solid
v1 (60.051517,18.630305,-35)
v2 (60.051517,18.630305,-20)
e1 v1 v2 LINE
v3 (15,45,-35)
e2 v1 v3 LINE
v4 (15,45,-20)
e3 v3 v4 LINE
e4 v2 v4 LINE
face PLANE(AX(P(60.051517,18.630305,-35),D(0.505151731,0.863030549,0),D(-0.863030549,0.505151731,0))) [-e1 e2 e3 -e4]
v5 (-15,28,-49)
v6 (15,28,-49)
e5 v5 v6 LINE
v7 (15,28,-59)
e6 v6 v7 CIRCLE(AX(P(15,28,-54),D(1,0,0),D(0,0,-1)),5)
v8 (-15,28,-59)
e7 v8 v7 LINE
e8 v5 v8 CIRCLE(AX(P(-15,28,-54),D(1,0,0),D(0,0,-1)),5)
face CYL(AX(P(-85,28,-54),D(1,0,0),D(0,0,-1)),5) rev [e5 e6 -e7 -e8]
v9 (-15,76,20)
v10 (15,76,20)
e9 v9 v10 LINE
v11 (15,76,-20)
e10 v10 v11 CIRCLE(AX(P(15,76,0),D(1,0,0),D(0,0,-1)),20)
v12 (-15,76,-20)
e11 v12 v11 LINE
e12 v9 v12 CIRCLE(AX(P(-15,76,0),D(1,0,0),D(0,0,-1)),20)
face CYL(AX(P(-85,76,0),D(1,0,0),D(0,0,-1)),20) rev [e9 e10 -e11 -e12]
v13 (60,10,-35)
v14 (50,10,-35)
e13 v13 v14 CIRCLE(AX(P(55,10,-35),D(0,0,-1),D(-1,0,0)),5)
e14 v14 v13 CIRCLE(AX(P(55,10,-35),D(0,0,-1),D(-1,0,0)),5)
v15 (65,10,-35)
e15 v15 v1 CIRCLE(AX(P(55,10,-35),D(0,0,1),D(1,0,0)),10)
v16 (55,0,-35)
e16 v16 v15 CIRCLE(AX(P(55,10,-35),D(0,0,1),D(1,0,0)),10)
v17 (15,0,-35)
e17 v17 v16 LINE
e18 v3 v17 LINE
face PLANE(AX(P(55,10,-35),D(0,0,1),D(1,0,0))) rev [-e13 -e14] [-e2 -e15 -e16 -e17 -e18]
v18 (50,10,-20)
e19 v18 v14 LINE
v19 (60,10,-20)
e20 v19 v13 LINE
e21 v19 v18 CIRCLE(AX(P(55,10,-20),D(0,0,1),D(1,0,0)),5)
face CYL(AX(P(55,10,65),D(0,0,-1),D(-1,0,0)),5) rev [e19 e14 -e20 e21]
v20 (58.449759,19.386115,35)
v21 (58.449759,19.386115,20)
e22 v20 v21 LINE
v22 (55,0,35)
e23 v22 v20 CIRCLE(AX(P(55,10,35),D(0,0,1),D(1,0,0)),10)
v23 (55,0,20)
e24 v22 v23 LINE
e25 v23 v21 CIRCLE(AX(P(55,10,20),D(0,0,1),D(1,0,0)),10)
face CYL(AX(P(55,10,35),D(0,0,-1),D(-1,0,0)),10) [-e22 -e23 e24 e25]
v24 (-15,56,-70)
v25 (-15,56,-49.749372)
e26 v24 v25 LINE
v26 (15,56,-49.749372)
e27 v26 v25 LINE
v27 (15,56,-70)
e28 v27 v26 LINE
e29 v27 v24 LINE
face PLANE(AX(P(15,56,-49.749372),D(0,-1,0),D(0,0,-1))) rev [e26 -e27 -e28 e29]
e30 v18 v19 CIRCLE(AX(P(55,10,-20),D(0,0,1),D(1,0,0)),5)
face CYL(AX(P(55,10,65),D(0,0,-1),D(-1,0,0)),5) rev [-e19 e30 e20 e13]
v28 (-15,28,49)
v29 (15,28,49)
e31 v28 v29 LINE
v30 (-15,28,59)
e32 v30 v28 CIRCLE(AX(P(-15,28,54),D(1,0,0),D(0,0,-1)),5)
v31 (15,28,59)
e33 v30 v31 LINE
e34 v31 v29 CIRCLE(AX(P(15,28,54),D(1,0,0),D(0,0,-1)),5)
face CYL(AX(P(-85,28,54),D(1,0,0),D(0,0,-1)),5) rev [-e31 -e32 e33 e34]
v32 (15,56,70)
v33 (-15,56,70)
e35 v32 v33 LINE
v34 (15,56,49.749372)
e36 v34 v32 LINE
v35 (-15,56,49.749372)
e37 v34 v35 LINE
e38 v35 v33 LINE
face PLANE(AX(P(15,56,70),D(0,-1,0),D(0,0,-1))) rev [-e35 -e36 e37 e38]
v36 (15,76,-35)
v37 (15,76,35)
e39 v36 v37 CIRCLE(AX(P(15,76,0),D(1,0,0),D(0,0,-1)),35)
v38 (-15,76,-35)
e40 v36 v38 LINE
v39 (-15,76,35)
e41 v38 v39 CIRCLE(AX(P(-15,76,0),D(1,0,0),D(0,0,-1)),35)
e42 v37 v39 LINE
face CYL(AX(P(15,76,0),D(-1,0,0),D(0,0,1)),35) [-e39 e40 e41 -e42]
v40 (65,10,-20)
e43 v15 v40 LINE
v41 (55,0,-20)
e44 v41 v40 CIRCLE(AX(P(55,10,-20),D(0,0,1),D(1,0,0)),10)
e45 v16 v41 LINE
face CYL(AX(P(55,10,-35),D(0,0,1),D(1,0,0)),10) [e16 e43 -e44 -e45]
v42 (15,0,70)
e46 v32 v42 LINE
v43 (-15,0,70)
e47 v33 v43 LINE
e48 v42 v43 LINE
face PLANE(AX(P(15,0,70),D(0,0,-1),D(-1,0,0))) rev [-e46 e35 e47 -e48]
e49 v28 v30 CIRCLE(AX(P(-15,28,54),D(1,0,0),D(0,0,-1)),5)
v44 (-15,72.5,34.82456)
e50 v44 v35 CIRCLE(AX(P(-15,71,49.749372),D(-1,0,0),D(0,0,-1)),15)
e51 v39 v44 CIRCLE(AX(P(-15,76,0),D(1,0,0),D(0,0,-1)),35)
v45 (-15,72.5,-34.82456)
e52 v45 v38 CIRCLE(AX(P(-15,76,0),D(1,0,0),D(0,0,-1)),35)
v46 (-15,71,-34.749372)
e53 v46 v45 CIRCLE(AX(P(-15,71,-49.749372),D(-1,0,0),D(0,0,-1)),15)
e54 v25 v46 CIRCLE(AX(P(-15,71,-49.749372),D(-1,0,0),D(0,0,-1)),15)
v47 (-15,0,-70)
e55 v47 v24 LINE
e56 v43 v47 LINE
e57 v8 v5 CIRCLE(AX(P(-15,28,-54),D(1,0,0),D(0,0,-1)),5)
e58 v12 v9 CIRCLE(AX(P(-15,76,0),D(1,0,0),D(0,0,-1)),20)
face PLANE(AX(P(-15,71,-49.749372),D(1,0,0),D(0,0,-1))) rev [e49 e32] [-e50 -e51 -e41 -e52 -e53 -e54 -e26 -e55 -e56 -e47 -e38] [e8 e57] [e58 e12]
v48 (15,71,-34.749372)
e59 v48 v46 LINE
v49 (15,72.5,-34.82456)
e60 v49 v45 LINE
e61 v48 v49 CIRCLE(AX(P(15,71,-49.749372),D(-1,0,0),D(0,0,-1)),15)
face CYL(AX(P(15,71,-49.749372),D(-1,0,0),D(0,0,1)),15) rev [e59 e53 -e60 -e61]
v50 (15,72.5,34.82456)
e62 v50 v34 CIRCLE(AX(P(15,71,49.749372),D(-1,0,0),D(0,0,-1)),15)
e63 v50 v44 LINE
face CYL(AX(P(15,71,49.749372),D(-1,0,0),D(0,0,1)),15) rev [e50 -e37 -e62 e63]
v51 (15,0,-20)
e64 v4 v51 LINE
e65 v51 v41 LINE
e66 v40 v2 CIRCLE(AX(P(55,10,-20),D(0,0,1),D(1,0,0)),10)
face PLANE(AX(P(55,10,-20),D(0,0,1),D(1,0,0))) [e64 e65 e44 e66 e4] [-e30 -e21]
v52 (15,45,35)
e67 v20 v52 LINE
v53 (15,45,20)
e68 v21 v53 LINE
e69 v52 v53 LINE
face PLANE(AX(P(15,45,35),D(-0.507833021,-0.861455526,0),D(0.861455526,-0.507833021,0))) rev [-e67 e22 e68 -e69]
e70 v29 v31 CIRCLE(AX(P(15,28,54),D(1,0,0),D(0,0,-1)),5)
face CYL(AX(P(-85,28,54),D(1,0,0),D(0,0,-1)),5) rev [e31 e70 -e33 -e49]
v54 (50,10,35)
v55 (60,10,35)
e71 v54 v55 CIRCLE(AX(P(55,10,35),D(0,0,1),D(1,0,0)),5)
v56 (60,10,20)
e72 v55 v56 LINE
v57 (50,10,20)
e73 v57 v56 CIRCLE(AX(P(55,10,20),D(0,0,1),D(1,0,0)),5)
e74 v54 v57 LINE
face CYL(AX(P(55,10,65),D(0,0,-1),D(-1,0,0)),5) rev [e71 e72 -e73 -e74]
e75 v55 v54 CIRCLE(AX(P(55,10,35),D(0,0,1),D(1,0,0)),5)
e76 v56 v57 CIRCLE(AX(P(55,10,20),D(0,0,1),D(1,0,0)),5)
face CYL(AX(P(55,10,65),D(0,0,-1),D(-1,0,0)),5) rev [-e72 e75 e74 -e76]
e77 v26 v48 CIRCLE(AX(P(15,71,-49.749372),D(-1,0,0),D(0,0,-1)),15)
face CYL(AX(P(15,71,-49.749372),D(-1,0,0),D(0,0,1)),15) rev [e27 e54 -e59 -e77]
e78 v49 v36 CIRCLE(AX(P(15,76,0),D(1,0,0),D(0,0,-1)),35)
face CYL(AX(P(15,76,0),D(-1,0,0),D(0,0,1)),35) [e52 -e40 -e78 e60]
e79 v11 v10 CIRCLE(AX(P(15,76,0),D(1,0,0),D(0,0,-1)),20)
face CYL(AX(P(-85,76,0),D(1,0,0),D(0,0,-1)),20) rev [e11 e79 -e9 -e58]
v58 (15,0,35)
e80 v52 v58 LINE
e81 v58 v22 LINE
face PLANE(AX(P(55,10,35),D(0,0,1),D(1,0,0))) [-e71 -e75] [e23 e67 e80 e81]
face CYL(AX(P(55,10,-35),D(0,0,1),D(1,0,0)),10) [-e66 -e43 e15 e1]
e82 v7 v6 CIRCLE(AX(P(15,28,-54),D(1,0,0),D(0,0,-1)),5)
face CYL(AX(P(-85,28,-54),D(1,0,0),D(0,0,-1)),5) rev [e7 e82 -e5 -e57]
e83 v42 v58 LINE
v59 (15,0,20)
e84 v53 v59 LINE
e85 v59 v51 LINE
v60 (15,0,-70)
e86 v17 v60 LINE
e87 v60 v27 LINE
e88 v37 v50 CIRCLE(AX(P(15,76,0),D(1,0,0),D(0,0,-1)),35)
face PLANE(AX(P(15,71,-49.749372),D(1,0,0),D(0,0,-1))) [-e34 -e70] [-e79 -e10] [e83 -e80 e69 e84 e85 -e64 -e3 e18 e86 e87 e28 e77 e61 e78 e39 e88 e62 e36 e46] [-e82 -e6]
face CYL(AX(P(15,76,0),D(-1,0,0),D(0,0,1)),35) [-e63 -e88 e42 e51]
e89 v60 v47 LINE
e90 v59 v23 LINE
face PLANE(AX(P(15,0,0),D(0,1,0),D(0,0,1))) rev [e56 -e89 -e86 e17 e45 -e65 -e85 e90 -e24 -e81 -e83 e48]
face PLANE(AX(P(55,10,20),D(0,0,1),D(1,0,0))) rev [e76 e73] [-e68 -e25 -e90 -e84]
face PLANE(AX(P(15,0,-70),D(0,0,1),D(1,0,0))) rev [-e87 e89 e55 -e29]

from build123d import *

# Parameters (mm, degrees)
PILLOW_BLOCK_BASE_DEPTH = 15
LUG_ARM_1_DEPTH         = 15
LUG_START               = -15
LUG_ARM_2_DEPTH         = 15
LUG_PIN_HOLE_SKETCH_R   = 5
LUG_PIN_HOLE_DEPTH      = 100
MOUNTING_HOLES_SKETCH_R = 5
MOUNTING_HOLES_2X_DEPTH = 100
SHAFT_BORE_SKETCH_R     = 20
SHAFT_BORE_DEPTH        = 100


with BuildPart() as part:
    # Base Profile Sketch → Pillow Block Base (new, symmetric)
    with BuildSketch(Plane(origin=(0, 0, 0), x_dir=(0, 0, -1), z_dir=(1, 0, 0))):
        with BuildLine():
            Line((0, 0), (-70, 0))
            Line((-70, 0), (-70, 56))
            Line((-70, 56), (-49.749371855, 56))
            ThreePointArc((-49.749371855, 56), (-38.625074125, 60.937694101), (-34.824560299, 72.5))
            ThreePointArc((-34.824560299, 72.5), (0, 111), (34.824560299, 72.5))
            ThreePointArc((34.824560299, 72.5), (38.625074125, 60.937694101), (49.749371855, 56))
            Line((49.749371855, 56), (70, 56))
            Line((70, 56), (70, 0))
            Line((70, 0), (0, 0))
        make_face()
    extrude(amount=PILLOW_BLOCK_BASE_DEPTH, both=True)

    # Lug Arm 1 Sketch → Lug Arm 1 (add)
    with BuildSketch(Plane.XY.offset(20)):
        with BuildLine():
            Line((15, 0), (55, 0))
            ThreePointArc((55, 0), (64.845332755, 8.248023132), (58.449759048, 19.386115411))
            Line((58.449759048, 19.386115411), (15, 45))
            Line((15, 45), (15, 0))
        make_face()
    extrude(amount=LUG_ARM_1_DEPTH)

    # Lug Arm 2 Sketch → Lug Arm 2 (add)
    with BuildSketch(Plane.XY.offset(-20).offset(LUG_START)):
        with BuildLine():
            Line((15, 0), (55, 0))
            ThreePointArc((55, 0), (64.651503897, 7.383041358), (60.051517306, 18.630305493))
            Line((60.051517306, 18.630305493), (15, 45))
            Line((15, 45), (15, 0))
        make_face()
    extrude(amount=LUG_ARM_2_DEPTH)

    # Lug Pin Hole Sketch → Lug Pin Hole (cut)
    with BuildSketch(Plane(origin=(0, 0, -35), x_dir=(-1, 0, 0), z_dir=(0, 0, -1))):
        with Locations((-55, 10)):
            Circle(LUG_PIN_HOLE_SKETCH_R)
    extrude(amount=-LUG_PIN_HOLE_DEPTH, mode=Mode.SUBTRACT)

    # Mounting Holes Sketch → Mounting Holes 2x (cut)
    with BuildSketch(Plane(origin=(15, 0, 0), x_dir=(0, 0, -1), z_dir=(1, 0, 0))):
        with Locations((-54, 28)):
            Circle(MOUNTING_HOLES_SKETCH_R)
        with Locations((54, 28)):
            Circle(MOUNTING_HOLES_SKETCH_R)
    extrude(amount=-MOUNTING_HOLES_2X_DEPTH, mode=Mode.SUBTRACT)

    # Shaft Bore Sketch → Shaft Bore (cut)
    with BuildSketch(Plane(origin=(15, 0, 0), x_dir=(0, 0, -1), z_dir=(1, 0, 0))):
        with Locations((0, 76)):
            Circle(SHAFT_BORE_SKETCH_R)
    extrude(amount=-SHAFT_BORE_DEPTH, mode=Mode.SUBTRACT)


solid = part.part
